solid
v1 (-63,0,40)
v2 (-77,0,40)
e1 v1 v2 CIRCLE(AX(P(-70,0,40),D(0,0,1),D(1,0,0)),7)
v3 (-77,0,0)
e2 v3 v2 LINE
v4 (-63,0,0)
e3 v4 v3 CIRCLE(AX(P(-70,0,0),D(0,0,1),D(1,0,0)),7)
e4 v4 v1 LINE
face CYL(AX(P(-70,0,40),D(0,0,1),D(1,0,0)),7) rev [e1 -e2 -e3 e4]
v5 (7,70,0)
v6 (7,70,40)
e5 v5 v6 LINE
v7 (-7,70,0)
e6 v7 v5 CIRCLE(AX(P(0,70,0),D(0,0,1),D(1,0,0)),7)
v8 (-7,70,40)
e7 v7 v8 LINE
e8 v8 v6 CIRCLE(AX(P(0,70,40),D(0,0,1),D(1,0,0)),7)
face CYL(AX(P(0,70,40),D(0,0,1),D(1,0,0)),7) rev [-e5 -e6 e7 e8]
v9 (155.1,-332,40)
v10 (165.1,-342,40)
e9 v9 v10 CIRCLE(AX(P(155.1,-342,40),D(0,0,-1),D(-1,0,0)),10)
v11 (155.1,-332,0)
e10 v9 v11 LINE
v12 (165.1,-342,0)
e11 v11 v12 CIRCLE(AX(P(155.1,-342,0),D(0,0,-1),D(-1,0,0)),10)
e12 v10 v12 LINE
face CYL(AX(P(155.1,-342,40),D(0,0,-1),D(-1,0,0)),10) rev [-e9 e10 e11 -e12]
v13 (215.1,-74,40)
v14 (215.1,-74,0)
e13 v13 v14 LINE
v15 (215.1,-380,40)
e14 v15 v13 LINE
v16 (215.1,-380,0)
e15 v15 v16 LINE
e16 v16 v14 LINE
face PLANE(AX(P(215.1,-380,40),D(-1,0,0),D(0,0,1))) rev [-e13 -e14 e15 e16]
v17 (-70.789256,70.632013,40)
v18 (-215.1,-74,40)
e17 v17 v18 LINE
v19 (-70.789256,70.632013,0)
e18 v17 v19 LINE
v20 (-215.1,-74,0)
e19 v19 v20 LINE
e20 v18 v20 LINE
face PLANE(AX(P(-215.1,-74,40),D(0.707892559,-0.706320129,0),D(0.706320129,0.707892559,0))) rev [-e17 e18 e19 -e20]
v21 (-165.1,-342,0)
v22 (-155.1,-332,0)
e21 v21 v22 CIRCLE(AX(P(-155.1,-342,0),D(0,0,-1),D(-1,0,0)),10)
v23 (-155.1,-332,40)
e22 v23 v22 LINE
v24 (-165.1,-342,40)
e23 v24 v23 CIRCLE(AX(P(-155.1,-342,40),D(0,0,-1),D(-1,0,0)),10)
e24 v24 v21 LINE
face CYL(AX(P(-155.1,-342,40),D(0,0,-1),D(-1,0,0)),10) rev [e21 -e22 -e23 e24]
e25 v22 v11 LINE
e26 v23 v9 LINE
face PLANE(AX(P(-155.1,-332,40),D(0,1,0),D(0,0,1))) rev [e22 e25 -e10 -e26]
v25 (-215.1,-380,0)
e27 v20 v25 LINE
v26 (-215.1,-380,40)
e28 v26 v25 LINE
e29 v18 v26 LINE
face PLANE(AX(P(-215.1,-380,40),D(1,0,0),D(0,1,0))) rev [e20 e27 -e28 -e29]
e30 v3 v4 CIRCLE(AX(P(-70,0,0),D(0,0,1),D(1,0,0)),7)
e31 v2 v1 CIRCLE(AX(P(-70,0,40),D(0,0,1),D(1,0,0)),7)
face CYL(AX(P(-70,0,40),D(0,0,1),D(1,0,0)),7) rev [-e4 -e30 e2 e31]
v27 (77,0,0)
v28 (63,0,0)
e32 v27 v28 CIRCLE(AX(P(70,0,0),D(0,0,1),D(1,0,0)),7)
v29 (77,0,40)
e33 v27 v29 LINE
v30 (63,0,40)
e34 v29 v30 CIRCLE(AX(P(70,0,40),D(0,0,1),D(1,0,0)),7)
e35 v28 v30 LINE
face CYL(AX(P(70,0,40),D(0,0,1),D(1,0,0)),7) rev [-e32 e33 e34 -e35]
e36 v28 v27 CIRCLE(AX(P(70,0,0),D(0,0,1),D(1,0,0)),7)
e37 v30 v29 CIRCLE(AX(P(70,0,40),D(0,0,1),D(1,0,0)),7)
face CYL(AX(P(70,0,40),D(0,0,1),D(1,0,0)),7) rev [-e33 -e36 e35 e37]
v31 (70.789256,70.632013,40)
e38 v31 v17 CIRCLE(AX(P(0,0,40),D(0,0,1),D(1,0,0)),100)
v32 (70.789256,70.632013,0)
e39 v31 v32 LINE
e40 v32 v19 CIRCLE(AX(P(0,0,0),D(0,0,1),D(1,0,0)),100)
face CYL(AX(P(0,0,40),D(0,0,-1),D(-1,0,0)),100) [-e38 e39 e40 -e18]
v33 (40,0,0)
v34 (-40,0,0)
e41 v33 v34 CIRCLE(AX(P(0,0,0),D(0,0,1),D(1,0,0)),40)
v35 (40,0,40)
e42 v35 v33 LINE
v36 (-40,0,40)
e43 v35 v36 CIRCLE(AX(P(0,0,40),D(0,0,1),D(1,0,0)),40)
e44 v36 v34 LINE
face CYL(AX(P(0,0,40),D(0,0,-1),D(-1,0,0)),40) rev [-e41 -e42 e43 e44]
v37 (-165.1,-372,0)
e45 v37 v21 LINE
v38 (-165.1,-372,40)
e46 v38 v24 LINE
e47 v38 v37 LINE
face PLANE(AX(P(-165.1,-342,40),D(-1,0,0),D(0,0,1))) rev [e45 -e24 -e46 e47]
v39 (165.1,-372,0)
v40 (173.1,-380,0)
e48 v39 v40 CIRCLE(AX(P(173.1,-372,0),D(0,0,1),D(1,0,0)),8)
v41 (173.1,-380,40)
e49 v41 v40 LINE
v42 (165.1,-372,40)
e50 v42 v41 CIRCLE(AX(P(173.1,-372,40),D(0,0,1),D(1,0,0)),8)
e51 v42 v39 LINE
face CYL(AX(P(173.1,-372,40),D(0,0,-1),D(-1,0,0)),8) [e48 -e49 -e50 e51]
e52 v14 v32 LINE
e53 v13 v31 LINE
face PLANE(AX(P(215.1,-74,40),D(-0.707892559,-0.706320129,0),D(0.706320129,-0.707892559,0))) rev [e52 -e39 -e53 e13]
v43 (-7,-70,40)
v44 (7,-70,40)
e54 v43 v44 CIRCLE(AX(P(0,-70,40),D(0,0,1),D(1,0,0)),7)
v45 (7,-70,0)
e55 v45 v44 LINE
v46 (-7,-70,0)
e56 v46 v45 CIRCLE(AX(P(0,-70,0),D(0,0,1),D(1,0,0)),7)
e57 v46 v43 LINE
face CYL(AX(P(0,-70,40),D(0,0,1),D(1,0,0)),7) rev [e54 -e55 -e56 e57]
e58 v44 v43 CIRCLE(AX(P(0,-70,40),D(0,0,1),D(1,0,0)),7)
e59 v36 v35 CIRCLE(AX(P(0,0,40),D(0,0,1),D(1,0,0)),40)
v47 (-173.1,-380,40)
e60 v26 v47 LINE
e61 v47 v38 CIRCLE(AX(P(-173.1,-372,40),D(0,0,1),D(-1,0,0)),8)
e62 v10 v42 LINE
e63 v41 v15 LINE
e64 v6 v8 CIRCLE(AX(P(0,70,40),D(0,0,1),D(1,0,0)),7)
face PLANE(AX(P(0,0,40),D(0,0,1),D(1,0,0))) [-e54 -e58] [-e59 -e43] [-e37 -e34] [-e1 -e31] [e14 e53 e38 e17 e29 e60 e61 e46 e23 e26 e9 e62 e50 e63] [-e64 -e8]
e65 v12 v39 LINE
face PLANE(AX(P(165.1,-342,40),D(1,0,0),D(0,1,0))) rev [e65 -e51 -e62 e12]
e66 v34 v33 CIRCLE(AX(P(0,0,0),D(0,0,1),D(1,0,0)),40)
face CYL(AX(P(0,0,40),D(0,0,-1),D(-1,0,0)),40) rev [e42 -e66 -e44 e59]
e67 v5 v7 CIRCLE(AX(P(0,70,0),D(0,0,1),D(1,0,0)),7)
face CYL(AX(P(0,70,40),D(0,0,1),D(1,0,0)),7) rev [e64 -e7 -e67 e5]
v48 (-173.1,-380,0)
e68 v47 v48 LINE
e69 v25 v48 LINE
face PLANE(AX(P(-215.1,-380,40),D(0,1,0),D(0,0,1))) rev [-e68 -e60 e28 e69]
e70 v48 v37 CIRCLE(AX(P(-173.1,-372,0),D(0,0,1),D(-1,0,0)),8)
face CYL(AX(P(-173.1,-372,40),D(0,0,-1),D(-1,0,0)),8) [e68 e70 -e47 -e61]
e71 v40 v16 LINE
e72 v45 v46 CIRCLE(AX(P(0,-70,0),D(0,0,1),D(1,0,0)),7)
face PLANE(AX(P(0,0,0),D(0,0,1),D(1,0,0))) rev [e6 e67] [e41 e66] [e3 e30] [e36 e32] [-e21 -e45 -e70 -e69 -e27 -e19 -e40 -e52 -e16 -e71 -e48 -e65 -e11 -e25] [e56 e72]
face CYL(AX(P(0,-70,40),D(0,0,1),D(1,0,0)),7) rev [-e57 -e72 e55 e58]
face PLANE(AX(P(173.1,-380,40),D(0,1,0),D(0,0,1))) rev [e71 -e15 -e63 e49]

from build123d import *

# Parameters (mm, degrees)
SKETCH1_R           = 40
BOSS_EXTRUDE1_DEPTH = 40
M16_TAPPED_HOLE1_D  = 14


with BuildPart() as part:
    # Sketch1 → Boss-Extrude1 (new body)
    with BuildSketch(Plane.XY):
        with BuildLine():
            Line((-215.1, -380), (-173.1, -380))
            ThreePointArc((-173.1, -380), (-167.443145751, -377.656854249), (-165.1, -372))
            Line((-165.1, -372), (-165.1, -342))
            ThreePointArc((-165.1, -342), (-162.171067812, -334.928932188), (-155.1, -332))
            Line((-155.1, -332), (155.1, -332))
            ThreePointArc((155.1, -332), (162.171067812, -334.928932188), (165.1, -342))
            Line((165.1, -342), (165.1, -372))
            ThreePointArc((165.1, -372), (167.443145751, -377.656854249), (173.1, -380))
            Line((173.1, -380), (215.1, -380))
            Line((215.1, -380), (215.1, -74))
            Line((215.1, -74), (70.789255941, 70.632012878))
            ThreePointArc((70.789255941, 70.632012878), (0, 100), (-70.789255941, 70.632012878))
            Line((-70.789255941, 70.632012878), (-215.1, -74))
            Line((-215.1, -74), (-215.1, -380))
        make_face()
        Circle(SKETCH1_R, mode=Mode.SUBTRACT)
    extrude(amount=BOSS_EXTRUDE1_DEPTH)

    # M16 Tapped Hole1 (through all)
    with Locations(Plane.XY.offset(40)):
        with Locations((0, 70), (70, 0), (0, -70), (-70, 0)):
            Hole(M16_TAPPED_HOLE1_D / 2)


solid = part.part
